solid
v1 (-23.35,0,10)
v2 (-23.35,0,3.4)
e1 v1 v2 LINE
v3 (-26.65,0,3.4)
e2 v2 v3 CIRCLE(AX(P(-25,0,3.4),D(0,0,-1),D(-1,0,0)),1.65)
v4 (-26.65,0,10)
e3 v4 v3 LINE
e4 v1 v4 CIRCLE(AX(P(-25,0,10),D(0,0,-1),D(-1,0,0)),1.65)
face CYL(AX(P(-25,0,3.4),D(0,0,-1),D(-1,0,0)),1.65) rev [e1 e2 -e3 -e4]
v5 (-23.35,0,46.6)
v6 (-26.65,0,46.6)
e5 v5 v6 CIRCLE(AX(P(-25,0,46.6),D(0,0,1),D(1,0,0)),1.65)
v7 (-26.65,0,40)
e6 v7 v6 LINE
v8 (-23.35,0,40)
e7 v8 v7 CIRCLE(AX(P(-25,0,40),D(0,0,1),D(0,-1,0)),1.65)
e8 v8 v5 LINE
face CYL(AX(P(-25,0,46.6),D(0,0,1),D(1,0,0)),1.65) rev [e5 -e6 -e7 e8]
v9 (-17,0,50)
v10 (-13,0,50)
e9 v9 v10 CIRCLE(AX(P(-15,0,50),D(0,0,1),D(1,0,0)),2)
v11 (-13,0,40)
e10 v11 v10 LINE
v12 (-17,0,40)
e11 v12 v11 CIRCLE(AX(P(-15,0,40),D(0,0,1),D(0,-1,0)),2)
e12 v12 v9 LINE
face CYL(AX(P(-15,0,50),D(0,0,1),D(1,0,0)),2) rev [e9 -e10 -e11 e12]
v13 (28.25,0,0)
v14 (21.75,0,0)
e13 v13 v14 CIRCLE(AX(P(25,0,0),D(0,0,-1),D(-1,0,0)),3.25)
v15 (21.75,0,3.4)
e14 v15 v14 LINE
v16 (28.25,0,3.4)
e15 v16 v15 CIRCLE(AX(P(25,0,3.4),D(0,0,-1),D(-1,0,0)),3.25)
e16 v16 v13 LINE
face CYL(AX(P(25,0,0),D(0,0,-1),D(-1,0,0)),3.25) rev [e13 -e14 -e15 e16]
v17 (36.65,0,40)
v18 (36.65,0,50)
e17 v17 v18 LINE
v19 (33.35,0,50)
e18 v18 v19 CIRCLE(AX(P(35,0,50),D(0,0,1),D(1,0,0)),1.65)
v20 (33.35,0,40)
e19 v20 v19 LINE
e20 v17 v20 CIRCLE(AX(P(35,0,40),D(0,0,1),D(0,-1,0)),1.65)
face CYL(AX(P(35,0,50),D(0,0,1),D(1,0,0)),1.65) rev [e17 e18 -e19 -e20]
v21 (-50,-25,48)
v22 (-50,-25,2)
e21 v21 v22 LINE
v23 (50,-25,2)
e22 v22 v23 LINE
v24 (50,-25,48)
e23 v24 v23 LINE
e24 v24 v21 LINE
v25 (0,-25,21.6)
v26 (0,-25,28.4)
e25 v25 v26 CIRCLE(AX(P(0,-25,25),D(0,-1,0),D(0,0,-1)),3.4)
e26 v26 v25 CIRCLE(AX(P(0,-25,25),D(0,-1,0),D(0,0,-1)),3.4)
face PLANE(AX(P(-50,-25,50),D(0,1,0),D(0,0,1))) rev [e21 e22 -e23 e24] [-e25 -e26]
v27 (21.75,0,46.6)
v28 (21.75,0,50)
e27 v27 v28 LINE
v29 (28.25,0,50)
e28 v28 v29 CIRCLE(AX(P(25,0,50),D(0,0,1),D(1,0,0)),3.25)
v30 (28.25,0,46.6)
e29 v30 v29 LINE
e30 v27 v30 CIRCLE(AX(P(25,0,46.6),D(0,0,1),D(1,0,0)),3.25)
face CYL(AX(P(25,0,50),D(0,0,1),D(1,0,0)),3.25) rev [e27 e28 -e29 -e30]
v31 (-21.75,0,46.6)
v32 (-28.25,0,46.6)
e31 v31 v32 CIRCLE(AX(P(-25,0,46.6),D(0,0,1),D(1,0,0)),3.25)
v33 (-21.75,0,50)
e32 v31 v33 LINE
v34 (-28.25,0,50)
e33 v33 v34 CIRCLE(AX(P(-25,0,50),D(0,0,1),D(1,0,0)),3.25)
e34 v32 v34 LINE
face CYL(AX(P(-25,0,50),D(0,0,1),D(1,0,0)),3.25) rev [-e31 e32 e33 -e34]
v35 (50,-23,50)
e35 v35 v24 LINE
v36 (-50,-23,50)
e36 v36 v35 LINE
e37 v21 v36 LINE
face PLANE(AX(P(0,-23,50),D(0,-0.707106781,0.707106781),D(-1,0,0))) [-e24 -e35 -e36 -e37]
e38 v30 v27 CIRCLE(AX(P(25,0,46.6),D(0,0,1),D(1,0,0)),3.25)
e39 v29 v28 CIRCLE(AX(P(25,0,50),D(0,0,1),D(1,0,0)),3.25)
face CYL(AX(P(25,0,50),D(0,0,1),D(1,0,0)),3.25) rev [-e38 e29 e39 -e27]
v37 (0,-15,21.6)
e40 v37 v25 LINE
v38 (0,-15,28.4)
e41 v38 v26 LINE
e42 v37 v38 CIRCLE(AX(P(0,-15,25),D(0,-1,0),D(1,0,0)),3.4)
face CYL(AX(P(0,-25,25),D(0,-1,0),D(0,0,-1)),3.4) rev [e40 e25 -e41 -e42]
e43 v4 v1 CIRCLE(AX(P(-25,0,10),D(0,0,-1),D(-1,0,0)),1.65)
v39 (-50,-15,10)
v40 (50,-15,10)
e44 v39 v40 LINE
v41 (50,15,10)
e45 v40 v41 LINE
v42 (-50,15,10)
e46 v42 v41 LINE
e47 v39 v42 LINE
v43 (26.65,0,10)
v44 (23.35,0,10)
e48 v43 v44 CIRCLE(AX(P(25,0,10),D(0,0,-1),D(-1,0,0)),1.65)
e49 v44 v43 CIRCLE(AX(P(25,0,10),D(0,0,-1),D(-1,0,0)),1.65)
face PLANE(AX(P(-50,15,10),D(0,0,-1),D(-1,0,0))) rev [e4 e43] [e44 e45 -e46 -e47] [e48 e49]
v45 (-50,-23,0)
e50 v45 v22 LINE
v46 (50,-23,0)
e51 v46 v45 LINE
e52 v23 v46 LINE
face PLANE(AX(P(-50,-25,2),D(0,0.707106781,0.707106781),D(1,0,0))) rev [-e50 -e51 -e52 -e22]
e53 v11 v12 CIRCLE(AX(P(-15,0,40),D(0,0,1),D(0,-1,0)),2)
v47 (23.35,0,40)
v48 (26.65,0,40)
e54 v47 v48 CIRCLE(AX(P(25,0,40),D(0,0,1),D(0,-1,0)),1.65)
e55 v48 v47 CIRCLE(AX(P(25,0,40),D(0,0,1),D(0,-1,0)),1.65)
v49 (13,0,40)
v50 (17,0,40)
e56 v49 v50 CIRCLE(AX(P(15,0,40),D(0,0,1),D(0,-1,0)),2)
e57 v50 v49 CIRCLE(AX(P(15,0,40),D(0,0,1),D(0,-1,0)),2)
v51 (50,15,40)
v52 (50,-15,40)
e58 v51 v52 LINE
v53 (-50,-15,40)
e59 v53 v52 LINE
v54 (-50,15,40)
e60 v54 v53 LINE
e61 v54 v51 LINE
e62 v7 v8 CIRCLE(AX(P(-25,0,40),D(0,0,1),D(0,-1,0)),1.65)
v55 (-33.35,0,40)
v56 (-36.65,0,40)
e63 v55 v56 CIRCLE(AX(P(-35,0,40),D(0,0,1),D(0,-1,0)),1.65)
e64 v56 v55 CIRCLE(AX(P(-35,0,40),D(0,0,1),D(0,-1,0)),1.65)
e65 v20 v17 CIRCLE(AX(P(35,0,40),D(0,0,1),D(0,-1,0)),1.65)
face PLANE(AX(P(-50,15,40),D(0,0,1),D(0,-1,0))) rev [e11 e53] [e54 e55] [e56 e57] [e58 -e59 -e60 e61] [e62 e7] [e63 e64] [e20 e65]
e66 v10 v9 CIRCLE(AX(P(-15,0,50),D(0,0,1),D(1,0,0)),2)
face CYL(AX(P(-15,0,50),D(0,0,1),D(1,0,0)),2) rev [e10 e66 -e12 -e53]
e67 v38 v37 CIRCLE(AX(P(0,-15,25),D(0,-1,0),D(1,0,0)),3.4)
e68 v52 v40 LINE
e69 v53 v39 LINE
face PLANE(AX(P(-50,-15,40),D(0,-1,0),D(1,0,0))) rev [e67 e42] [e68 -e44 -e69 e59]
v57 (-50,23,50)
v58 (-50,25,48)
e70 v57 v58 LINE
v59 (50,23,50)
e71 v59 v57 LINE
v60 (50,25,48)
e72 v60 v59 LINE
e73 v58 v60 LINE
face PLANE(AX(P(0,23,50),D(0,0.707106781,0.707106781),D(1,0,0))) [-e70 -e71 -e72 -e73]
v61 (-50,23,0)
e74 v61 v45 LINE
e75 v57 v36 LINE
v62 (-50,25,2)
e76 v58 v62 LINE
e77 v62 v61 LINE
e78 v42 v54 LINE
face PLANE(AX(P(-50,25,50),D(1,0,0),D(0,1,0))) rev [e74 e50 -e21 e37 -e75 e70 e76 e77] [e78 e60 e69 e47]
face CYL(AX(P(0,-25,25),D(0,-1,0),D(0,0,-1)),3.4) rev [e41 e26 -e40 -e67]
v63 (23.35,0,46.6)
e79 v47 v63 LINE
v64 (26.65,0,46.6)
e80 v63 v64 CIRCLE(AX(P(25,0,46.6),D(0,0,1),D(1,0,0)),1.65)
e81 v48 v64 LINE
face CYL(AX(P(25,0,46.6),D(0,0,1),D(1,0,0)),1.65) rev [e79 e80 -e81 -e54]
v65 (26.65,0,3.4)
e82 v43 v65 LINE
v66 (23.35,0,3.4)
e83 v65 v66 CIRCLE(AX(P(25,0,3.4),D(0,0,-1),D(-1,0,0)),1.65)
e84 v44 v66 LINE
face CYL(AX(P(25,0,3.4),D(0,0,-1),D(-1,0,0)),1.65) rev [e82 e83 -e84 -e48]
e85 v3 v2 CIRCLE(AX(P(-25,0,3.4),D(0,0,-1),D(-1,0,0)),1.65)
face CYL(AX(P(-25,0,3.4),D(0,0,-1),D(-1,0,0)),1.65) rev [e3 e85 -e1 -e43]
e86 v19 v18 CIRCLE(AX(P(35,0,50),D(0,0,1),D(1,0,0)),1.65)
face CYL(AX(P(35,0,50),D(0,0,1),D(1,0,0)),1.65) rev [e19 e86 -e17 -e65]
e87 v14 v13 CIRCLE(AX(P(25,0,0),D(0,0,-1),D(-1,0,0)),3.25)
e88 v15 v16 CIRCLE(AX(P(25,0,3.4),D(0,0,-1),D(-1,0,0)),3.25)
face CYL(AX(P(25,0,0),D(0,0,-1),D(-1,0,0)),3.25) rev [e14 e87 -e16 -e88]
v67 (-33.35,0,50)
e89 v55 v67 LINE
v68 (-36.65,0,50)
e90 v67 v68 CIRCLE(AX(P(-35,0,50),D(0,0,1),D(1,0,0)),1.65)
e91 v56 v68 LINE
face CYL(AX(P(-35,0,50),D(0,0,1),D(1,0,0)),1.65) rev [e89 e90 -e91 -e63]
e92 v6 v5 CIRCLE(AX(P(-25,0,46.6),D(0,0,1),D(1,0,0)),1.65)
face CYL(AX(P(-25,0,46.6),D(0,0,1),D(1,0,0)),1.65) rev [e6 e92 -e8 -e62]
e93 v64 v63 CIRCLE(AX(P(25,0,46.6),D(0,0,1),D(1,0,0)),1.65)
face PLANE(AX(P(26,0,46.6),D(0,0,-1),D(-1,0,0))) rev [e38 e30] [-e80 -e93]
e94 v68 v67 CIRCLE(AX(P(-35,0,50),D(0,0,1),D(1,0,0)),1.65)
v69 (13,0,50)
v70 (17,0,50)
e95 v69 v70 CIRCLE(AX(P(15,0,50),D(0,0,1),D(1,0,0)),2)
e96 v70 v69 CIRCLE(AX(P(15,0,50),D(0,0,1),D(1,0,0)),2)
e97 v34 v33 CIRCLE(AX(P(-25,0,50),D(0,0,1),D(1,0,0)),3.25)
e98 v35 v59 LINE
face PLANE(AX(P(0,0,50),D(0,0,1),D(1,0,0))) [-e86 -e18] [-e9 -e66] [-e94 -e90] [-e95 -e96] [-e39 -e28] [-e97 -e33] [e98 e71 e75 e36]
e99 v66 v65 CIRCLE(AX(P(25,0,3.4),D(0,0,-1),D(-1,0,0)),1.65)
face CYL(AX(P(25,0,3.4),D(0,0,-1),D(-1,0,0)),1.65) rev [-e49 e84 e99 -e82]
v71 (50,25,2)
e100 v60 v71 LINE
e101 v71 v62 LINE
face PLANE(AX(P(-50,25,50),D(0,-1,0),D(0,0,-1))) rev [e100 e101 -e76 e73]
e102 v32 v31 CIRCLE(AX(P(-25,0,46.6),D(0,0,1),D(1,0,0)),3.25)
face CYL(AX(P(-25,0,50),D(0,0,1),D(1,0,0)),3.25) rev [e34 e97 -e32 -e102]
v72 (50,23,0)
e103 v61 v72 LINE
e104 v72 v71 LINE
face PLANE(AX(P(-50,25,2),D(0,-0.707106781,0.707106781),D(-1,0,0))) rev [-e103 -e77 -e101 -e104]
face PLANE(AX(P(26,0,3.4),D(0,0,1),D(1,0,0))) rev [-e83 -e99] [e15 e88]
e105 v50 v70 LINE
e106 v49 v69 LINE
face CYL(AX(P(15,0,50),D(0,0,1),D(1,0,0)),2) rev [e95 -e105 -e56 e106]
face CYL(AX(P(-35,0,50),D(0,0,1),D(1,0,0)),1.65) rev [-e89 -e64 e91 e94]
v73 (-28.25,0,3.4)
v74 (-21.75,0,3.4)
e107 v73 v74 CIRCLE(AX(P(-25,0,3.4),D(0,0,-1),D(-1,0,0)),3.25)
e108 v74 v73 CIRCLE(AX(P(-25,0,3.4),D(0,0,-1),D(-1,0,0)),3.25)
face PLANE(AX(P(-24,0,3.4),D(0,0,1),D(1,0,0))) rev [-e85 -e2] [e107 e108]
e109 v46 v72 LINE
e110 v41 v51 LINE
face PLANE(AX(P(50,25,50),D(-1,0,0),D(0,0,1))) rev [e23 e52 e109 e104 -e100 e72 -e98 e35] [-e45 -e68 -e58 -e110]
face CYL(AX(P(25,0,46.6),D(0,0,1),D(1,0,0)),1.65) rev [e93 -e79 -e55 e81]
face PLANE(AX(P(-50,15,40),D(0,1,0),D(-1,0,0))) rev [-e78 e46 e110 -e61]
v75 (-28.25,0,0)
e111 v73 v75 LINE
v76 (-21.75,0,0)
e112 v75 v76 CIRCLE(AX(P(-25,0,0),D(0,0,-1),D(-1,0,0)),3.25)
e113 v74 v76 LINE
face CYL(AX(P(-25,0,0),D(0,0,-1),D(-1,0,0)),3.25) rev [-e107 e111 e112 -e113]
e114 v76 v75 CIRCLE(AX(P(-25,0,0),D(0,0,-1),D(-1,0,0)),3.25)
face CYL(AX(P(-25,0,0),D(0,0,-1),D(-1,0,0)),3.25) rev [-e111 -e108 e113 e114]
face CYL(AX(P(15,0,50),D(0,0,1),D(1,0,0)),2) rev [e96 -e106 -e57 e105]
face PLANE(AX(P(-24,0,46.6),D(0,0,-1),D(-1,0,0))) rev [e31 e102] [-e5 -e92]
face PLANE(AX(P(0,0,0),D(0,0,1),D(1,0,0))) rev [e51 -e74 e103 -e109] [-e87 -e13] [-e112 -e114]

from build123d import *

# Parameters (mm, degrees)
SKETCH1_W                                           = 100
SKETCH1_H                                           = 50
BOSS_EXTRUDE1_DEPTH                                 = 50
SKETCH2_W                                           = 30
SKETCH2_H                                           = 30
CUT_EXTRUDE1_DEPTH                                  = 115.564392374
CBORE_FOR_M3_HEX_SOCKET_HEAD_CAP_SCREW1_D           = 2
CBORE_FOR_M3_HEX_SOCKET_HEAD_CAP_SCREW1_DEPTH       = 10
CBORE_FOR_M3_HEX_SOCKET_HEAD_CAP_SCREW1_CBORE_D     = 6.5
CBORE_FOR_M3_HEX_SOCKET_HEAD_CAP_SCREW1_CBORE_DEPTH = 3.4
CBORE_FOR_M3_HEX_SOCKET_HEAD_CAP_SCREW2_D           = 2
CBORE_FOR_M3_HEX_SOCKET_HEAD_CAP_SCREW2_CBORE_D     = 6.5
CBORE_FOR_M3_HEX_SOCKET_HEAD_CAP_SCREW2_CBORE_DEPTH = 3.4
M4_TAPPED_HOLE1_D                                   = 3.3
M4_TAPPED_HOLE1_DEPTH                               = 10.1
M4_TAPPED_HOLE1_TIP                                 = 0.991420021
F_4_0_4_DIAMETER_HOLE1_D                            = 4
F_4_0_4_DIAMETER_HOLE1_DEPTH                        = 10
CHAMFER1_SIZE                                       = 2
M8_TAPPED_HOLE1_D                                   = 6.8
M8_TAPPED_HOLE1_DEPTH                               = 19.75
M8_TAPPED_HOLE1_TIP                                 = 2.042926105
M4_TAPPED_HOLE2_D                                   = 3.3
M4_TAPPED_HOLE2_DEPTH                               = 10.1
M4_TAPPED_HOLE2_TIP                                 = 0.991420021
M4_TAPPED_HOLE3_D                                   = 3.3
M4_TAPPED_HOLE3_DEPTH                               = 10.1
M4_TAPPED_HOLE3_TIP                                 = 0.991420021


with BuildPart() as part:
    # Sketch1 → Boss-Extrude1 (new body)
    with BuildSketch(Plane.XY):
        Rectangle(SKETCH1_W, SKETCH1_H)
    extrude(amount=BOSS_EXTRUDE1_DEPTH)

    # Sketch2 → Cut-Extrude1 (cut, through all)
    with BuildSketch(Plane(origin=(50, 0, 0), x_dir=(0, 0, -1), z_dir=(1, 0, 0))):
        with Locations((-25, 0)):
            Rectangle(SKETCH2_W, SKETCH2_H)
    extrude(amount=-CUT_EXTRUDE1_DEPTH, mode=Mode.SUBTRACT)

    # CBORE for M3 Hex Socket Head Cap Screw1
    with Locations(Plane(origin=(0, 0, 0), x_dir=(-1, 0, 0), z_dir=(0, 0, -1))):
        with Locations((-25, 0), (25, 0)):
            CounterBoreHole(CBORE_FOR_M3_HEX_SOCKET_HEAD_CAP_SCREW1_D / 2, CBORE_FOR_M3_HEX_SOCKET_HEAD_CAP_SCREW1_CBORE_D / 2, CBORE_FOR_M3_HEX_SOCKET_HEAD_CAP_SCREW1_CBORE_DEPTH, depth=CBORE_FOR_M3_HEX_SOCKET_HEAD_CAP_SCREW1_DEPTH)

    # CBORE for M3 Hex Socket Head Cap Screw2 (through all)
    with Locations(Plane.XY.offset(50)):
        with Locations((-25, 0), (25, 0)):
            CounterBoreHole(CBORE_FOR_M3_HEX_SOCKET_HEAD_CAP_SCREW2_D / 2, CBORE_FOR_M3_HEX_SOCKET_HEAD_CAP_SCREW2_CBORE_D / 2, CBORE_FOR_M3_HEX_SOCKET_HEAD_CAP_SCREW2_CBORE_DEPTH)

    # M4 Tapped Hole1
    with Locations(Plane.XY.offset(50)):
        with Locations((-35, 0), (35, 0)):
            Hole(M4_TAPPED_HOLE1_D / 2, depth=M4_TAPPED_HOLE1_DEPTH)
            with Locations((0, 0, -(M4_TAPPED_HOLE1_DEPTH + M4_TAPPED_HOLE1_TIP / 2))):  # 118° drill point
                Cone(0, M4_TAPPED_HOLE1_D / 2, M4_TAPPED_HOLE1_TIP, mode=Mode.SUBTRACT)

    # Ø4.0 (4) Diameter Hole1
    with Locations(Plane.XY.offset(50)):
        with Locations((15, 0), (-15, 0)):
            Hole(F_4_0_4_DIAMETER_HOLE1_D / 2, depth=F_4_0_4_DIAMETER_HOLE1_DEPTH)

    # Chamfer1
    chamfer1_edges = [part.edges().sort_by_distance(p)[0] for p in [
        (0, -25, 50),
        (0, -25, 0),
        (0, 25, 0),
        (0, 25, 50),
    ]]
    chamfer(chamfer1_edges, length=CHAMFER1_SIZE)

    # M8 Tapped Hole1
    with Locations(Plane(origin=(0, -25, 0), x_dir=(-1, 0, 0), z_dir=(0, -1, 0))):
        with Locations((0, -25)):
            Hole(M8_TAPPED_HOLE1_D / 2, depth=M8_TAPPED_HOLE1_DEPTH)
            with Locations((0, 0, -(M8_TAPPED_HOLE1_DEPTH + M8_TAPPED_HOLE1_TIP / 2))):  # 118° drill point
                Cone(0, M8_TAPPED_HOLE1_D / 2, M8_TAPPED_HOLE1_TIP, mode=Mode.SUBTRACT)

    # M4 Tapped Hole2
    with Locations(Plane(origin=(0, 0, 3.4), x_dir=(-1, 0, 0), z_dir=(0, 0, -1))):
        with Locations((-25, 0), (25, 0)):
            Hole(M4_TAPPED_HOLE2_D / 2, depth=M4_TAPPED_HOLE2_DEPTH)
            with Locations((0, 0, -(M4_TAPPED_HOLE2_DEPTH + M4_TAPPED_HOLE2_TIP / 2))):  # 118° drill point
                Cone(0, M4_TAPPED_HOLE2_D / 2, M4_TAPPED_HOLE2_TIP, mode=Mode.SUBTRACT)

    # M4 Tapped Hole3
    with Locations(Plane.XY.offset(46.6)):
        with Locations((-25, 0), (25, 0)):
            Hole(M4_TAPPED_HOLE3_D / 2, depth=M4_TAPPED_HOLE3_DEPTH)
            with Locations((0, 0, -(M4_TAPPED_HOLE3_DEPTH + M4_TAPPED_HOLE3_TIP / 2))):  # 118° drill point
                Cone(0, M4_TAPPED_HOLE3_D / 2, M4_TAPPED_HOLE3_TIP, mode=Mode.SUBTRACT)


solid = part.part
